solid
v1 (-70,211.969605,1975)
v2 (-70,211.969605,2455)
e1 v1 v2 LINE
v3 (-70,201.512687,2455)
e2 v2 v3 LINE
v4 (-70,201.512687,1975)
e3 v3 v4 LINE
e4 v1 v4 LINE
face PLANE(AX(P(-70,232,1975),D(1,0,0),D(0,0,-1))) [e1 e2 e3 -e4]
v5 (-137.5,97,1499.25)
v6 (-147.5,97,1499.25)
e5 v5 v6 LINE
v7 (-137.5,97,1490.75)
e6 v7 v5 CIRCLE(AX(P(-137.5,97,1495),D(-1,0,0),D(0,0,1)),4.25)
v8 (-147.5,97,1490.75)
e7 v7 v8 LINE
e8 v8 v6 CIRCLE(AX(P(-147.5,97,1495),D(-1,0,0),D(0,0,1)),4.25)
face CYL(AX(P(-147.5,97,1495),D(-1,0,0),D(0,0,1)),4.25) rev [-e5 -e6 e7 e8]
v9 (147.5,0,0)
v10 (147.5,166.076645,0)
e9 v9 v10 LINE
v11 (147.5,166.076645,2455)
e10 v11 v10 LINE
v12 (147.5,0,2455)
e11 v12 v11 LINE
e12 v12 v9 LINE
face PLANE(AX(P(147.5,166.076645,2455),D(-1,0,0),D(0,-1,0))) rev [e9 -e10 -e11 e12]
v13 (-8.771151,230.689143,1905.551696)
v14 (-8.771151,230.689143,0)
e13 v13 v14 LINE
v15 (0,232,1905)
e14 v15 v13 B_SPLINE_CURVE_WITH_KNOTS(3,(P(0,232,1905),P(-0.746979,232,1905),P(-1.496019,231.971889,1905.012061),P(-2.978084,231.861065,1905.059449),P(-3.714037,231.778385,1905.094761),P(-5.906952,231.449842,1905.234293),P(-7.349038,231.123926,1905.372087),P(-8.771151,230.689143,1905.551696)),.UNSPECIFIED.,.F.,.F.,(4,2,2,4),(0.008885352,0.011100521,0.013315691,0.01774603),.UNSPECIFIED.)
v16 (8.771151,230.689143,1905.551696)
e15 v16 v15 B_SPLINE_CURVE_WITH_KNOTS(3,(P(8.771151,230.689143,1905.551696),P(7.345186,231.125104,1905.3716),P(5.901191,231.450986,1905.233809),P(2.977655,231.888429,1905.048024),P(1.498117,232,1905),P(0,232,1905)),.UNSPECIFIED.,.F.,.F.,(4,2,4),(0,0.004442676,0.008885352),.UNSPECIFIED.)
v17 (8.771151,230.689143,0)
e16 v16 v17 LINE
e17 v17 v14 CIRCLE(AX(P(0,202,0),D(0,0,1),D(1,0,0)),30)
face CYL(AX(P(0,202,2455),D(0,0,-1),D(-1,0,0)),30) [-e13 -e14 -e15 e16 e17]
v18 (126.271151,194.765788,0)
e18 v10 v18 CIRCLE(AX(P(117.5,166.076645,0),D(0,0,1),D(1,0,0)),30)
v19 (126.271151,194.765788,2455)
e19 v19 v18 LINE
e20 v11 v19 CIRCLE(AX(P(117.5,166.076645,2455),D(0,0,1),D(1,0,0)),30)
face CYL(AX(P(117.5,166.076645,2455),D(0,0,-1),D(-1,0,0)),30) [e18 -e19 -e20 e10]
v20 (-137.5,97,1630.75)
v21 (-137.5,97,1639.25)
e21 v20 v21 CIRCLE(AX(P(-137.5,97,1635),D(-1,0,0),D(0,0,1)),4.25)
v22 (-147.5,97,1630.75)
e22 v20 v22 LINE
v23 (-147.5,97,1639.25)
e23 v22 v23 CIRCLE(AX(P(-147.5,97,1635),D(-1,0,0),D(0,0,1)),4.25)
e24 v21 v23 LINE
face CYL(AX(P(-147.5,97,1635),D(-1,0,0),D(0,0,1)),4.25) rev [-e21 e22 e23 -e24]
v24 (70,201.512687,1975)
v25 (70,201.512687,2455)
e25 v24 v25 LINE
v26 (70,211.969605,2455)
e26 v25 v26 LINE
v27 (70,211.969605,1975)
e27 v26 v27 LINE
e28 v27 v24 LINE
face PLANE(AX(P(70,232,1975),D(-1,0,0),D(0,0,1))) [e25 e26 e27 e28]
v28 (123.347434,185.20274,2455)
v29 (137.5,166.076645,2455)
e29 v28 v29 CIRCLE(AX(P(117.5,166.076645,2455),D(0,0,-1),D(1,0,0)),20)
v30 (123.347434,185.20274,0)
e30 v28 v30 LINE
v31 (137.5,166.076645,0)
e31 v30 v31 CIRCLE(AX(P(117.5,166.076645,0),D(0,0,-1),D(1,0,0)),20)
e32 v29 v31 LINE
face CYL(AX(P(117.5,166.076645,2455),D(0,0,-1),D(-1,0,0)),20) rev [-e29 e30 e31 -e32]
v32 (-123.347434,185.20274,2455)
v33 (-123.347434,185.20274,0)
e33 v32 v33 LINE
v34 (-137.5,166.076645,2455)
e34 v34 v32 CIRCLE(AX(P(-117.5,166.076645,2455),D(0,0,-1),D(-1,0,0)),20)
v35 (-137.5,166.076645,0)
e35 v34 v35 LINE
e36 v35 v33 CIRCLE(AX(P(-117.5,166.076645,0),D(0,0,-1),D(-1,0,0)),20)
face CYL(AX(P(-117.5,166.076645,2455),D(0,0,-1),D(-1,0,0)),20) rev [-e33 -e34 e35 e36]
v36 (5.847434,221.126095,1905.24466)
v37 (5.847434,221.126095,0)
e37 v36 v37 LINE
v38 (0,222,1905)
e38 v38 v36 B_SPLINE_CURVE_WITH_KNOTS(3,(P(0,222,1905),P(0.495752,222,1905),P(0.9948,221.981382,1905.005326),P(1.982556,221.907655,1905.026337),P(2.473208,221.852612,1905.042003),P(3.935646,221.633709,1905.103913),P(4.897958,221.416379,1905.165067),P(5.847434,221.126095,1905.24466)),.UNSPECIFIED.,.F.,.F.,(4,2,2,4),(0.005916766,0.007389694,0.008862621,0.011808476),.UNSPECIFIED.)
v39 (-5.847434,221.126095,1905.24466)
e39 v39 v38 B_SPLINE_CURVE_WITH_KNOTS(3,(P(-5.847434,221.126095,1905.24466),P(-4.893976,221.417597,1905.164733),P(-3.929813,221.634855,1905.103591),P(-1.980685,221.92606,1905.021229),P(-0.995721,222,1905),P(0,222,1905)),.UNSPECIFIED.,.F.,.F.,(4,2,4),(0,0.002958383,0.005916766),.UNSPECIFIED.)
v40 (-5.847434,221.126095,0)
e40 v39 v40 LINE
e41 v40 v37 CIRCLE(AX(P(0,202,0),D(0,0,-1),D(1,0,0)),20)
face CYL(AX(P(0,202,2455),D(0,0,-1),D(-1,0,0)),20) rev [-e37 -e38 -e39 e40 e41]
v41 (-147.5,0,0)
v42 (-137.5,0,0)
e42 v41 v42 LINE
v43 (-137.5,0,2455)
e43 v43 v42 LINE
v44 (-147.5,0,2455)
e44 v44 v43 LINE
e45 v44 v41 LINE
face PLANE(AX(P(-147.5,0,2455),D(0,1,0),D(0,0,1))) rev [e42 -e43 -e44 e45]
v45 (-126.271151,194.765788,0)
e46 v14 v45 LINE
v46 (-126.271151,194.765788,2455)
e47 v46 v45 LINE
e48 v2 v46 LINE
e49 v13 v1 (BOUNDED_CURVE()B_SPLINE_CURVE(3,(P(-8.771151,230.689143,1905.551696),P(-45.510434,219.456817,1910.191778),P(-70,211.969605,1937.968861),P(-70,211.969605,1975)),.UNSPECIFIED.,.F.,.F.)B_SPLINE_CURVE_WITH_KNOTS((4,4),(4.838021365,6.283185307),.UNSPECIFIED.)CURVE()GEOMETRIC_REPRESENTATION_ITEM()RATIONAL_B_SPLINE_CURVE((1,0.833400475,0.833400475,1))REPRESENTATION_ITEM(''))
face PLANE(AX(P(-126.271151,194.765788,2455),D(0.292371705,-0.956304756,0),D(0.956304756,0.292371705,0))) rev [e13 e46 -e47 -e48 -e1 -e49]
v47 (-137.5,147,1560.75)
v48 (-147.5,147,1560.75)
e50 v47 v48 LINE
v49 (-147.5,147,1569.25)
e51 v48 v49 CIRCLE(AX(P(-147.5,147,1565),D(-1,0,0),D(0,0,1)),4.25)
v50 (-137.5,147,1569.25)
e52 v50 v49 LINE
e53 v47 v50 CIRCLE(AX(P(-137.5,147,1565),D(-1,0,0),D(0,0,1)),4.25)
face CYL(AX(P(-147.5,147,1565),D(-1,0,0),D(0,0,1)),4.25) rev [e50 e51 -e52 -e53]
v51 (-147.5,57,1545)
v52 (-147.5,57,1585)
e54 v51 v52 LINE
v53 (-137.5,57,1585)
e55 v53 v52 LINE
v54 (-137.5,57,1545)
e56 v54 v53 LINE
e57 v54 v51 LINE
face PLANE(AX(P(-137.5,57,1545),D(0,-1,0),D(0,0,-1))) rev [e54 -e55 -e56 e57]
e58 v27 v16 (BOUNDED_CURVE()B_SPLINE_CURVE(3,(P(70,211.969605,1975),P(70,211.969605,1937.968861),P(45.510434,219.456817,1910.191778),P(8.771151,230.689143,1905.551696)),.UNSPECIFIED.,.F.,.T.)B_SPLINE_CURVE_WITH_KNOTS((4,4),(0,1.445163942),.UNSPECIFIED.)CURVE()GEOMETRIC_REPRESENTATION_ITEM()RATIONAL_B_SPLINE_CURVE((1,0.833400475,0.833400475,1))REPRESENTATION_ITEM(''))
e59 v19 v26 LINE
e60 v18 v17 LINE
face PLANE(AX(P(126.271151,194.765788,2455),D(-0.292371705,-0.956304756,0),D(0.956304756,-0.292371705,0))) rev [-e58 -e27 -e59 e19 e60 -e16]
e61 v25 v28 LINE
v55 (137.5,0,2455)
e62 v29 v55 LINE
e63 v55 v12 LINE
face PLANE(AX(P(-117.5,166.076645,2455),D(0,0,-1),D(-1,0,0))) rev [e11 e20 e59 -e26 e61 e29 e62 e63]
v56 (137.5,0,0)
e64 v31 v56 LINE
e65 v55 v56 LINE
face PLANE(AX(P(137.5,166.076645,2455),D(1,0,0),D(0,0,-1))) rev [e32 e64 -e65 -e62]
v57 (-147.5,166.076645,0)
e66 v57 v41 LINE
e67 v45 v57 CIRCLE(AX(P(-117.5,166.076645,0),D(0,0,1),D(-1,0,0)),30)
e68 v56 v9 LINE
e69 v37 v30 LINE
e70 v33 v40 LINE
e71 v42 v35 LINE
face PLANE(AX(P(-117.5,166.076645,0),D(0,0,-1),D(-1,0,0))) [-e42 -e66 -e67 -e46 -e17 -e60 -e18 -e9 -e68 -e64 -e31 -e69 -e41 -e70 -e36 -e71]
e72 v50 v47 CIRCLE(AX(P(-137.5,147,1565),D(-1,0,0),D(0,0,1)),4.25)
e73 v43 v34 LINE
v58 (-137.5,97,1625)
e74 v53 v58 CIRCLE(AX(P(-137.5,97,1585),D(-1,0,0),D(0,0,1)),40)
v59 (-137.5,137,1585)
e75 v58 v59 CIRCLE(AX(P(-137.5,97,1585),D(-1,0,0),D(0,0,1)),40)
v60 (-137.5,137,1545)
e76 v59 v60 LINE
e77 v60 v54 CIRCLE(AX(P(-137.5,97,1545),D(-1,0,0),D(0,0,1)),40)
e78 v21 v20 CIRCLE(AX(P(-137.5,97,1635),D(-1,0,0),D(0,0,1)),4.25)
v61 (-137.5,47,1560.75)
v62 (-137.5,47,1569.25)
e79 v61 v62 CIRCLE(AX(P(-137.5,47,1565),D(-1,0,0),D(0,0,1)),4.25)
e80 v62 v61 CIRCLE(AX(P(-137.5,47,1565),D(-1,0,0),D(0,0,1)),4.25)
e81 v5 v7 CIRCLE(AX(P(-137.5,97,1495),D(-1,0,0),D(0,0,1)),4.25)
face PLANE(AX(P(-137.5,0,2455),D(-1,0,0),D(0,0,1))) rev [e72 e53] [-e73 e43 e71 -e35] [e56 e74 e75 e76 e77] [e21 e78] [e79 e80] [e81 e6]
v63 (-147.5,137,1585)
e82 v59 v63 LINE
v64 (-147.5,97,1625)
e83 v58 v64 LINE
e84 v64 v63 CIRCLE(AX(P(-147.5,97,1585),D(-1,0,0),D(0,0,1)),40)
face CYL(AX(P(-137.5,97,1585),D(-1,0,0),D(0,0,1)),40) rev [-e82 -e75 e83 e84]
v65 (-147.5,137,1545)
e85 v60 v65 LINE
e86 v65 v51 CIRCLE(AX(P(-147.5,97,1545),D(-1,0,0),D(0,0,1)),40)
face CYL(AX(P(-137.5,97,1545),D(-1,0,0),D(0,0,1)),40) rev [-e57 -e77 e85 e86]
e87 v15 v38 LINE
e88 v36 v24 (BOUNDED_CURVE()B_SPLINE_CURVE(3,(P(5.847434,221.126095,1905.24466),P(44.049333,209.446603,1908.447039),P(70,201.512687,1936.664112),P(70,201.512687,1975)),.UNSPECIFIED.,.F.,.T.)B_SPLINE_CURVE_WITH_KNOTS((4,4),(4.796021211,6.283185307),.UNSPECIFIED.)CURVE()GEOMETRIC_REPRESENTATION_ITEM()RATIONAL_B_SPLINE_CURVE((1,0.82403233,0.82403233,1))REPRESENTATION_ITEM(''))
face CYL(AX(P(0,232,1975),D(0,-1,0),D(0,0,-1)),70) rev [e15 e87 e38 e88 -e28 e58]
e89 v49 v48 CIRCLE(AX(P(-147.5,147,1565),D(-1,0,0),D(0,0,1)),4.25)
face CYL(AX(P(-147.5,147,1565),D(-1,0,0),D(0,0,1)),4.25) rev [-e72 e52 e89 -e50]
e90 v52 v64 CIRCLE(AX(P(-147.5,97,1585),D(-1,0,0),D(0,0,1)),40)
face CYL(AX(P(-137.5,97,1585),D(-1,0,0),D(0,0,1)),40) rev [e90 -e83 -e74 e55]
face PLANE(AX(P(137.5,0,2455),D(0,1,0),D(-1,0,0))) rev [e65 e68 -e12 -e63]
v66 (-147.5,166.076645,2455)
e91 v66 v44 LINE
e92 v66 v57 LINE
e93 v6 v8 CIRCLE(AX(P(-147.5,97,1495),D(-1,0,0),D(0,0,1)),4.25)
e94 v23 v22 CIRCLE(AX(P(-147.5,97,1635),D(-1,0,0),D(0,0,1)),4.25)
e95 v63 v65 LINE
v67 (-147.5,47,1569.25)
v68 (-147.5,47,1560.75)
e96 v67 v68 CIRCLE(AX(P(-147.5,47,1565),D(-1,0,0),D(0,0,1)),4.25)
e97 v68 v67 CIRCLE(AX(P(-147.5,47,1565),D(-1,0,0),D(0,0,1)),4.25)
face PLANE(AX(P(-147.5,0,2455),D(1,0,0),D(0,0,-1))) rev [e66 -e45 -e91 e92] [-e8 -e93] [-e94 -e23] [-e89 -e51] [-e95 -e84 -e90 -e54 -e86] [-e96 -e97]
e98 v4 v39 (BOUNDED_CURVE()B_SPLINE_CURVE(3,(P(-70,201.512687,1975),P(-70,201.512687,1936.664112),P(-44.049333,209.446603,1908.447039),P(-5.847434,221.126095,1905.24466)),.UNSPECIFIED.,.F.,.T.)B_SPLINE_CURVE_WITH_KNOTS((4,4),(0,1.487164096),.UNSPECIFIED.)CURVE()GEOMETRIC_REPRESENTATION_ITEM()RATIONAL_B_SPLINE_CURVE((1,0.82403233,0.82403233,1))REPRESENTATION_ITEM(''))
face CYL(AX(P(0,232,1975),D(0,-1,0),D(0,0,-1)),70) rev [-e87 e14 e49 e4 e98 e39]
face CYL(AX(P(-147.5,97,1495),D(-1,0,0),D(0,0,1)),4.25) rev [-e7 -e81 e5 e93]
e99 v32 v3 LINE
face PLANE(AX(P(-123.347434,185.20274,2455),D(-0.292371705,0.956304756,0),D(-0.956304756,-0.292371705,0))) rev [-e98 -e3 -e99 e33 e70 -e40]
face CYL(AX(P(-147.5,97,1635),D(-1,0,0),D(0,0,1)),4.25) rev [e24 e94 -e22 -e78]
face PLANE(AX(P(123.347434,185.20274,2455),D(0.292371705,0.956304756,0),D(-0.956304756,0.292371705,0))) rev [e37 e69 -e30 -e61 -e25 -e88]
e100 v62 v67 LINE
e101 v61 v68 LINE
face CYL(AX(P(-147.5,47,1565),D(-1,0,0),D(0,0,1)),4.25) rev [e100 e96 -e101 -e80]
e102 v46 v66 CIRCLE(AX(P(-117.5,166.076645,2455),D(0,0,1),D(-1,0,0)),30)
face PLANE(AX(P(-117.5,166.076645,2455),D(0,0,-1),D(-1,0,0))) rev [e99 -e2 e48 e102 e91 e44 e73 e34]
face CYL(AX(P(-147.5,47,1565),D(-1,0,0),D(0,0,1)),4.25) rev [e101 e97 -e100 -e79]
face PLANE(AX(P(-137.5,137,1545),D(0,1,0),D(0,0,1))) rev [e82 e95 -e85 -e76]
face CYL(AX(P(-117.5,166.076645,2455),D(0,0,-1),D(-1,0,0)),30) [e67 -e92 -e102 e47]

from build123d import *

# Parameters (mm, degrees)
BOSS_EXTRUDE1_DEPTH    = 2455
CUT_EXTRUDE1_DEPTH     = 2471.34516819
CUT_EXTRUDE2_DEPTH     = 10
M10_TAPPED_HOLE1_D     = 8.5
M10_TAPPED_HOLE1_DEPTH = 27.5
M10_TAPPED_HOLE1_TIP   = 2.553657631


with BuildPart() as part:
    # Sketch1 → Boss-Extrude1 (new body)
    with BuildSketch(Plane.XY):
        with BuildLine():
            Line((-147.5, 0), (-147.5, 166.076644929))
            ThreePointArc((-147.5, 166.076644929), (-141.615705819, 183.921328531), (-126.271151142, 194.765787607))
            Line((-126.271151142, 194.765787607), (-8.771151142, 230.689142679))
            ThreePointArc((-8.771151142, 230.689142679), (0, 232), (8.771151142, 230.689142679))
            Line((8.771151142, 230.689142679), (126.271151142, 194.765787607))
            ThreePointArc((126.271151142, 194.765787607), (141.615705819, 183.921328531), (147.5, 166.076644929))
            Line((147.5, 166.076644929), (147.5, 0))
            Line((147.5, 0), (137.5, 0))
            Line((137.5, 0), (137.5, 166.076644929))
            ThreePointArc((137.5, 166.076644929), (133.577137212, 177.973100664), (123.347434094, 185.202740048))
            Line((123.347434094, 185.202740048), (5.847434094, 221.126095119))
            ThreePointArc((5.847434094, 221.126095119), (0, 222), (-5.847434094, 221.126095119))
            Line((-5.847434094, 221.126095119), (-123.347434094, 185.202740048))
            ThreePointArc((-123.347434094, 185.202740048), (-133.577137212, 177.973100664), (-137.5, 166.076644929))
            Line((-137.5, 166.076644929), (-137.5, 0))
            Line((-137.5, 0), (-147.5, 0))
        make_face()
    extrude(amount=BOSS_EXTRUDE1_DEPTH)

    # Sketch2 → Cut-Extrude1 (cut, through all)
    with BuildSketch(Plane(origin=(0, 0, 0), x_dir=(1, 0, 0), z_dir=(0, 1, 0))):
        with BuildLine():
            Line((-70, -1975), (-70, -2455))
            Line((-70, -2455), (70, -2455))
            Line((70, -2455), (70, -1975))
            ThreePointArc((70, -1975), (0, -1905), (-70, -1975))
        make_face()
    extrude(amount=CUT_EXTRUDE1_DEPTH, mode=Mode.SUBTRACT)

    # Sketch3 → Cut-Extrude2 (cut)
    with BuildSketch(Plane.ZY.offset(147.5)):
        with BuildLine():
            Line((1545, 137), (1585, 137))
            ThreePointArc((1585, 137), (1625, 97), (1585, 57))
            Line((1585, 57), (1545, 57))
            ThreePointArc((1545, 57), (1505, 97), (1545, 137))
        make_face()
    extrude(amount=-CUT_EXTRUDE2_DEPTH, mode=Mode.SUBTRACT)

    # M10 Tapped Hole1
    with Locations(Plane.ZY.offset(147.5)):
        with Locations((1565, 147), (1565, 47), (1495, 97), (1635, 97)):
            Hole(M10_TAPPED_HOLE1_D / 2, depth=M10_TAPPED_HOLE1_DEPTH)
            with Locations((0, 0, -(M10_TAPPED_HOLE1_DEPTH + M10_TAPPED_HOLE1_TIP / 2))):  # 118° drill point
                Cone(0, M10_TAPPED_HOLE1_D / 2, M10_TAPPED_HOLE1_TIP, mode=Mode.SUBTRACT)


solid = part.part
